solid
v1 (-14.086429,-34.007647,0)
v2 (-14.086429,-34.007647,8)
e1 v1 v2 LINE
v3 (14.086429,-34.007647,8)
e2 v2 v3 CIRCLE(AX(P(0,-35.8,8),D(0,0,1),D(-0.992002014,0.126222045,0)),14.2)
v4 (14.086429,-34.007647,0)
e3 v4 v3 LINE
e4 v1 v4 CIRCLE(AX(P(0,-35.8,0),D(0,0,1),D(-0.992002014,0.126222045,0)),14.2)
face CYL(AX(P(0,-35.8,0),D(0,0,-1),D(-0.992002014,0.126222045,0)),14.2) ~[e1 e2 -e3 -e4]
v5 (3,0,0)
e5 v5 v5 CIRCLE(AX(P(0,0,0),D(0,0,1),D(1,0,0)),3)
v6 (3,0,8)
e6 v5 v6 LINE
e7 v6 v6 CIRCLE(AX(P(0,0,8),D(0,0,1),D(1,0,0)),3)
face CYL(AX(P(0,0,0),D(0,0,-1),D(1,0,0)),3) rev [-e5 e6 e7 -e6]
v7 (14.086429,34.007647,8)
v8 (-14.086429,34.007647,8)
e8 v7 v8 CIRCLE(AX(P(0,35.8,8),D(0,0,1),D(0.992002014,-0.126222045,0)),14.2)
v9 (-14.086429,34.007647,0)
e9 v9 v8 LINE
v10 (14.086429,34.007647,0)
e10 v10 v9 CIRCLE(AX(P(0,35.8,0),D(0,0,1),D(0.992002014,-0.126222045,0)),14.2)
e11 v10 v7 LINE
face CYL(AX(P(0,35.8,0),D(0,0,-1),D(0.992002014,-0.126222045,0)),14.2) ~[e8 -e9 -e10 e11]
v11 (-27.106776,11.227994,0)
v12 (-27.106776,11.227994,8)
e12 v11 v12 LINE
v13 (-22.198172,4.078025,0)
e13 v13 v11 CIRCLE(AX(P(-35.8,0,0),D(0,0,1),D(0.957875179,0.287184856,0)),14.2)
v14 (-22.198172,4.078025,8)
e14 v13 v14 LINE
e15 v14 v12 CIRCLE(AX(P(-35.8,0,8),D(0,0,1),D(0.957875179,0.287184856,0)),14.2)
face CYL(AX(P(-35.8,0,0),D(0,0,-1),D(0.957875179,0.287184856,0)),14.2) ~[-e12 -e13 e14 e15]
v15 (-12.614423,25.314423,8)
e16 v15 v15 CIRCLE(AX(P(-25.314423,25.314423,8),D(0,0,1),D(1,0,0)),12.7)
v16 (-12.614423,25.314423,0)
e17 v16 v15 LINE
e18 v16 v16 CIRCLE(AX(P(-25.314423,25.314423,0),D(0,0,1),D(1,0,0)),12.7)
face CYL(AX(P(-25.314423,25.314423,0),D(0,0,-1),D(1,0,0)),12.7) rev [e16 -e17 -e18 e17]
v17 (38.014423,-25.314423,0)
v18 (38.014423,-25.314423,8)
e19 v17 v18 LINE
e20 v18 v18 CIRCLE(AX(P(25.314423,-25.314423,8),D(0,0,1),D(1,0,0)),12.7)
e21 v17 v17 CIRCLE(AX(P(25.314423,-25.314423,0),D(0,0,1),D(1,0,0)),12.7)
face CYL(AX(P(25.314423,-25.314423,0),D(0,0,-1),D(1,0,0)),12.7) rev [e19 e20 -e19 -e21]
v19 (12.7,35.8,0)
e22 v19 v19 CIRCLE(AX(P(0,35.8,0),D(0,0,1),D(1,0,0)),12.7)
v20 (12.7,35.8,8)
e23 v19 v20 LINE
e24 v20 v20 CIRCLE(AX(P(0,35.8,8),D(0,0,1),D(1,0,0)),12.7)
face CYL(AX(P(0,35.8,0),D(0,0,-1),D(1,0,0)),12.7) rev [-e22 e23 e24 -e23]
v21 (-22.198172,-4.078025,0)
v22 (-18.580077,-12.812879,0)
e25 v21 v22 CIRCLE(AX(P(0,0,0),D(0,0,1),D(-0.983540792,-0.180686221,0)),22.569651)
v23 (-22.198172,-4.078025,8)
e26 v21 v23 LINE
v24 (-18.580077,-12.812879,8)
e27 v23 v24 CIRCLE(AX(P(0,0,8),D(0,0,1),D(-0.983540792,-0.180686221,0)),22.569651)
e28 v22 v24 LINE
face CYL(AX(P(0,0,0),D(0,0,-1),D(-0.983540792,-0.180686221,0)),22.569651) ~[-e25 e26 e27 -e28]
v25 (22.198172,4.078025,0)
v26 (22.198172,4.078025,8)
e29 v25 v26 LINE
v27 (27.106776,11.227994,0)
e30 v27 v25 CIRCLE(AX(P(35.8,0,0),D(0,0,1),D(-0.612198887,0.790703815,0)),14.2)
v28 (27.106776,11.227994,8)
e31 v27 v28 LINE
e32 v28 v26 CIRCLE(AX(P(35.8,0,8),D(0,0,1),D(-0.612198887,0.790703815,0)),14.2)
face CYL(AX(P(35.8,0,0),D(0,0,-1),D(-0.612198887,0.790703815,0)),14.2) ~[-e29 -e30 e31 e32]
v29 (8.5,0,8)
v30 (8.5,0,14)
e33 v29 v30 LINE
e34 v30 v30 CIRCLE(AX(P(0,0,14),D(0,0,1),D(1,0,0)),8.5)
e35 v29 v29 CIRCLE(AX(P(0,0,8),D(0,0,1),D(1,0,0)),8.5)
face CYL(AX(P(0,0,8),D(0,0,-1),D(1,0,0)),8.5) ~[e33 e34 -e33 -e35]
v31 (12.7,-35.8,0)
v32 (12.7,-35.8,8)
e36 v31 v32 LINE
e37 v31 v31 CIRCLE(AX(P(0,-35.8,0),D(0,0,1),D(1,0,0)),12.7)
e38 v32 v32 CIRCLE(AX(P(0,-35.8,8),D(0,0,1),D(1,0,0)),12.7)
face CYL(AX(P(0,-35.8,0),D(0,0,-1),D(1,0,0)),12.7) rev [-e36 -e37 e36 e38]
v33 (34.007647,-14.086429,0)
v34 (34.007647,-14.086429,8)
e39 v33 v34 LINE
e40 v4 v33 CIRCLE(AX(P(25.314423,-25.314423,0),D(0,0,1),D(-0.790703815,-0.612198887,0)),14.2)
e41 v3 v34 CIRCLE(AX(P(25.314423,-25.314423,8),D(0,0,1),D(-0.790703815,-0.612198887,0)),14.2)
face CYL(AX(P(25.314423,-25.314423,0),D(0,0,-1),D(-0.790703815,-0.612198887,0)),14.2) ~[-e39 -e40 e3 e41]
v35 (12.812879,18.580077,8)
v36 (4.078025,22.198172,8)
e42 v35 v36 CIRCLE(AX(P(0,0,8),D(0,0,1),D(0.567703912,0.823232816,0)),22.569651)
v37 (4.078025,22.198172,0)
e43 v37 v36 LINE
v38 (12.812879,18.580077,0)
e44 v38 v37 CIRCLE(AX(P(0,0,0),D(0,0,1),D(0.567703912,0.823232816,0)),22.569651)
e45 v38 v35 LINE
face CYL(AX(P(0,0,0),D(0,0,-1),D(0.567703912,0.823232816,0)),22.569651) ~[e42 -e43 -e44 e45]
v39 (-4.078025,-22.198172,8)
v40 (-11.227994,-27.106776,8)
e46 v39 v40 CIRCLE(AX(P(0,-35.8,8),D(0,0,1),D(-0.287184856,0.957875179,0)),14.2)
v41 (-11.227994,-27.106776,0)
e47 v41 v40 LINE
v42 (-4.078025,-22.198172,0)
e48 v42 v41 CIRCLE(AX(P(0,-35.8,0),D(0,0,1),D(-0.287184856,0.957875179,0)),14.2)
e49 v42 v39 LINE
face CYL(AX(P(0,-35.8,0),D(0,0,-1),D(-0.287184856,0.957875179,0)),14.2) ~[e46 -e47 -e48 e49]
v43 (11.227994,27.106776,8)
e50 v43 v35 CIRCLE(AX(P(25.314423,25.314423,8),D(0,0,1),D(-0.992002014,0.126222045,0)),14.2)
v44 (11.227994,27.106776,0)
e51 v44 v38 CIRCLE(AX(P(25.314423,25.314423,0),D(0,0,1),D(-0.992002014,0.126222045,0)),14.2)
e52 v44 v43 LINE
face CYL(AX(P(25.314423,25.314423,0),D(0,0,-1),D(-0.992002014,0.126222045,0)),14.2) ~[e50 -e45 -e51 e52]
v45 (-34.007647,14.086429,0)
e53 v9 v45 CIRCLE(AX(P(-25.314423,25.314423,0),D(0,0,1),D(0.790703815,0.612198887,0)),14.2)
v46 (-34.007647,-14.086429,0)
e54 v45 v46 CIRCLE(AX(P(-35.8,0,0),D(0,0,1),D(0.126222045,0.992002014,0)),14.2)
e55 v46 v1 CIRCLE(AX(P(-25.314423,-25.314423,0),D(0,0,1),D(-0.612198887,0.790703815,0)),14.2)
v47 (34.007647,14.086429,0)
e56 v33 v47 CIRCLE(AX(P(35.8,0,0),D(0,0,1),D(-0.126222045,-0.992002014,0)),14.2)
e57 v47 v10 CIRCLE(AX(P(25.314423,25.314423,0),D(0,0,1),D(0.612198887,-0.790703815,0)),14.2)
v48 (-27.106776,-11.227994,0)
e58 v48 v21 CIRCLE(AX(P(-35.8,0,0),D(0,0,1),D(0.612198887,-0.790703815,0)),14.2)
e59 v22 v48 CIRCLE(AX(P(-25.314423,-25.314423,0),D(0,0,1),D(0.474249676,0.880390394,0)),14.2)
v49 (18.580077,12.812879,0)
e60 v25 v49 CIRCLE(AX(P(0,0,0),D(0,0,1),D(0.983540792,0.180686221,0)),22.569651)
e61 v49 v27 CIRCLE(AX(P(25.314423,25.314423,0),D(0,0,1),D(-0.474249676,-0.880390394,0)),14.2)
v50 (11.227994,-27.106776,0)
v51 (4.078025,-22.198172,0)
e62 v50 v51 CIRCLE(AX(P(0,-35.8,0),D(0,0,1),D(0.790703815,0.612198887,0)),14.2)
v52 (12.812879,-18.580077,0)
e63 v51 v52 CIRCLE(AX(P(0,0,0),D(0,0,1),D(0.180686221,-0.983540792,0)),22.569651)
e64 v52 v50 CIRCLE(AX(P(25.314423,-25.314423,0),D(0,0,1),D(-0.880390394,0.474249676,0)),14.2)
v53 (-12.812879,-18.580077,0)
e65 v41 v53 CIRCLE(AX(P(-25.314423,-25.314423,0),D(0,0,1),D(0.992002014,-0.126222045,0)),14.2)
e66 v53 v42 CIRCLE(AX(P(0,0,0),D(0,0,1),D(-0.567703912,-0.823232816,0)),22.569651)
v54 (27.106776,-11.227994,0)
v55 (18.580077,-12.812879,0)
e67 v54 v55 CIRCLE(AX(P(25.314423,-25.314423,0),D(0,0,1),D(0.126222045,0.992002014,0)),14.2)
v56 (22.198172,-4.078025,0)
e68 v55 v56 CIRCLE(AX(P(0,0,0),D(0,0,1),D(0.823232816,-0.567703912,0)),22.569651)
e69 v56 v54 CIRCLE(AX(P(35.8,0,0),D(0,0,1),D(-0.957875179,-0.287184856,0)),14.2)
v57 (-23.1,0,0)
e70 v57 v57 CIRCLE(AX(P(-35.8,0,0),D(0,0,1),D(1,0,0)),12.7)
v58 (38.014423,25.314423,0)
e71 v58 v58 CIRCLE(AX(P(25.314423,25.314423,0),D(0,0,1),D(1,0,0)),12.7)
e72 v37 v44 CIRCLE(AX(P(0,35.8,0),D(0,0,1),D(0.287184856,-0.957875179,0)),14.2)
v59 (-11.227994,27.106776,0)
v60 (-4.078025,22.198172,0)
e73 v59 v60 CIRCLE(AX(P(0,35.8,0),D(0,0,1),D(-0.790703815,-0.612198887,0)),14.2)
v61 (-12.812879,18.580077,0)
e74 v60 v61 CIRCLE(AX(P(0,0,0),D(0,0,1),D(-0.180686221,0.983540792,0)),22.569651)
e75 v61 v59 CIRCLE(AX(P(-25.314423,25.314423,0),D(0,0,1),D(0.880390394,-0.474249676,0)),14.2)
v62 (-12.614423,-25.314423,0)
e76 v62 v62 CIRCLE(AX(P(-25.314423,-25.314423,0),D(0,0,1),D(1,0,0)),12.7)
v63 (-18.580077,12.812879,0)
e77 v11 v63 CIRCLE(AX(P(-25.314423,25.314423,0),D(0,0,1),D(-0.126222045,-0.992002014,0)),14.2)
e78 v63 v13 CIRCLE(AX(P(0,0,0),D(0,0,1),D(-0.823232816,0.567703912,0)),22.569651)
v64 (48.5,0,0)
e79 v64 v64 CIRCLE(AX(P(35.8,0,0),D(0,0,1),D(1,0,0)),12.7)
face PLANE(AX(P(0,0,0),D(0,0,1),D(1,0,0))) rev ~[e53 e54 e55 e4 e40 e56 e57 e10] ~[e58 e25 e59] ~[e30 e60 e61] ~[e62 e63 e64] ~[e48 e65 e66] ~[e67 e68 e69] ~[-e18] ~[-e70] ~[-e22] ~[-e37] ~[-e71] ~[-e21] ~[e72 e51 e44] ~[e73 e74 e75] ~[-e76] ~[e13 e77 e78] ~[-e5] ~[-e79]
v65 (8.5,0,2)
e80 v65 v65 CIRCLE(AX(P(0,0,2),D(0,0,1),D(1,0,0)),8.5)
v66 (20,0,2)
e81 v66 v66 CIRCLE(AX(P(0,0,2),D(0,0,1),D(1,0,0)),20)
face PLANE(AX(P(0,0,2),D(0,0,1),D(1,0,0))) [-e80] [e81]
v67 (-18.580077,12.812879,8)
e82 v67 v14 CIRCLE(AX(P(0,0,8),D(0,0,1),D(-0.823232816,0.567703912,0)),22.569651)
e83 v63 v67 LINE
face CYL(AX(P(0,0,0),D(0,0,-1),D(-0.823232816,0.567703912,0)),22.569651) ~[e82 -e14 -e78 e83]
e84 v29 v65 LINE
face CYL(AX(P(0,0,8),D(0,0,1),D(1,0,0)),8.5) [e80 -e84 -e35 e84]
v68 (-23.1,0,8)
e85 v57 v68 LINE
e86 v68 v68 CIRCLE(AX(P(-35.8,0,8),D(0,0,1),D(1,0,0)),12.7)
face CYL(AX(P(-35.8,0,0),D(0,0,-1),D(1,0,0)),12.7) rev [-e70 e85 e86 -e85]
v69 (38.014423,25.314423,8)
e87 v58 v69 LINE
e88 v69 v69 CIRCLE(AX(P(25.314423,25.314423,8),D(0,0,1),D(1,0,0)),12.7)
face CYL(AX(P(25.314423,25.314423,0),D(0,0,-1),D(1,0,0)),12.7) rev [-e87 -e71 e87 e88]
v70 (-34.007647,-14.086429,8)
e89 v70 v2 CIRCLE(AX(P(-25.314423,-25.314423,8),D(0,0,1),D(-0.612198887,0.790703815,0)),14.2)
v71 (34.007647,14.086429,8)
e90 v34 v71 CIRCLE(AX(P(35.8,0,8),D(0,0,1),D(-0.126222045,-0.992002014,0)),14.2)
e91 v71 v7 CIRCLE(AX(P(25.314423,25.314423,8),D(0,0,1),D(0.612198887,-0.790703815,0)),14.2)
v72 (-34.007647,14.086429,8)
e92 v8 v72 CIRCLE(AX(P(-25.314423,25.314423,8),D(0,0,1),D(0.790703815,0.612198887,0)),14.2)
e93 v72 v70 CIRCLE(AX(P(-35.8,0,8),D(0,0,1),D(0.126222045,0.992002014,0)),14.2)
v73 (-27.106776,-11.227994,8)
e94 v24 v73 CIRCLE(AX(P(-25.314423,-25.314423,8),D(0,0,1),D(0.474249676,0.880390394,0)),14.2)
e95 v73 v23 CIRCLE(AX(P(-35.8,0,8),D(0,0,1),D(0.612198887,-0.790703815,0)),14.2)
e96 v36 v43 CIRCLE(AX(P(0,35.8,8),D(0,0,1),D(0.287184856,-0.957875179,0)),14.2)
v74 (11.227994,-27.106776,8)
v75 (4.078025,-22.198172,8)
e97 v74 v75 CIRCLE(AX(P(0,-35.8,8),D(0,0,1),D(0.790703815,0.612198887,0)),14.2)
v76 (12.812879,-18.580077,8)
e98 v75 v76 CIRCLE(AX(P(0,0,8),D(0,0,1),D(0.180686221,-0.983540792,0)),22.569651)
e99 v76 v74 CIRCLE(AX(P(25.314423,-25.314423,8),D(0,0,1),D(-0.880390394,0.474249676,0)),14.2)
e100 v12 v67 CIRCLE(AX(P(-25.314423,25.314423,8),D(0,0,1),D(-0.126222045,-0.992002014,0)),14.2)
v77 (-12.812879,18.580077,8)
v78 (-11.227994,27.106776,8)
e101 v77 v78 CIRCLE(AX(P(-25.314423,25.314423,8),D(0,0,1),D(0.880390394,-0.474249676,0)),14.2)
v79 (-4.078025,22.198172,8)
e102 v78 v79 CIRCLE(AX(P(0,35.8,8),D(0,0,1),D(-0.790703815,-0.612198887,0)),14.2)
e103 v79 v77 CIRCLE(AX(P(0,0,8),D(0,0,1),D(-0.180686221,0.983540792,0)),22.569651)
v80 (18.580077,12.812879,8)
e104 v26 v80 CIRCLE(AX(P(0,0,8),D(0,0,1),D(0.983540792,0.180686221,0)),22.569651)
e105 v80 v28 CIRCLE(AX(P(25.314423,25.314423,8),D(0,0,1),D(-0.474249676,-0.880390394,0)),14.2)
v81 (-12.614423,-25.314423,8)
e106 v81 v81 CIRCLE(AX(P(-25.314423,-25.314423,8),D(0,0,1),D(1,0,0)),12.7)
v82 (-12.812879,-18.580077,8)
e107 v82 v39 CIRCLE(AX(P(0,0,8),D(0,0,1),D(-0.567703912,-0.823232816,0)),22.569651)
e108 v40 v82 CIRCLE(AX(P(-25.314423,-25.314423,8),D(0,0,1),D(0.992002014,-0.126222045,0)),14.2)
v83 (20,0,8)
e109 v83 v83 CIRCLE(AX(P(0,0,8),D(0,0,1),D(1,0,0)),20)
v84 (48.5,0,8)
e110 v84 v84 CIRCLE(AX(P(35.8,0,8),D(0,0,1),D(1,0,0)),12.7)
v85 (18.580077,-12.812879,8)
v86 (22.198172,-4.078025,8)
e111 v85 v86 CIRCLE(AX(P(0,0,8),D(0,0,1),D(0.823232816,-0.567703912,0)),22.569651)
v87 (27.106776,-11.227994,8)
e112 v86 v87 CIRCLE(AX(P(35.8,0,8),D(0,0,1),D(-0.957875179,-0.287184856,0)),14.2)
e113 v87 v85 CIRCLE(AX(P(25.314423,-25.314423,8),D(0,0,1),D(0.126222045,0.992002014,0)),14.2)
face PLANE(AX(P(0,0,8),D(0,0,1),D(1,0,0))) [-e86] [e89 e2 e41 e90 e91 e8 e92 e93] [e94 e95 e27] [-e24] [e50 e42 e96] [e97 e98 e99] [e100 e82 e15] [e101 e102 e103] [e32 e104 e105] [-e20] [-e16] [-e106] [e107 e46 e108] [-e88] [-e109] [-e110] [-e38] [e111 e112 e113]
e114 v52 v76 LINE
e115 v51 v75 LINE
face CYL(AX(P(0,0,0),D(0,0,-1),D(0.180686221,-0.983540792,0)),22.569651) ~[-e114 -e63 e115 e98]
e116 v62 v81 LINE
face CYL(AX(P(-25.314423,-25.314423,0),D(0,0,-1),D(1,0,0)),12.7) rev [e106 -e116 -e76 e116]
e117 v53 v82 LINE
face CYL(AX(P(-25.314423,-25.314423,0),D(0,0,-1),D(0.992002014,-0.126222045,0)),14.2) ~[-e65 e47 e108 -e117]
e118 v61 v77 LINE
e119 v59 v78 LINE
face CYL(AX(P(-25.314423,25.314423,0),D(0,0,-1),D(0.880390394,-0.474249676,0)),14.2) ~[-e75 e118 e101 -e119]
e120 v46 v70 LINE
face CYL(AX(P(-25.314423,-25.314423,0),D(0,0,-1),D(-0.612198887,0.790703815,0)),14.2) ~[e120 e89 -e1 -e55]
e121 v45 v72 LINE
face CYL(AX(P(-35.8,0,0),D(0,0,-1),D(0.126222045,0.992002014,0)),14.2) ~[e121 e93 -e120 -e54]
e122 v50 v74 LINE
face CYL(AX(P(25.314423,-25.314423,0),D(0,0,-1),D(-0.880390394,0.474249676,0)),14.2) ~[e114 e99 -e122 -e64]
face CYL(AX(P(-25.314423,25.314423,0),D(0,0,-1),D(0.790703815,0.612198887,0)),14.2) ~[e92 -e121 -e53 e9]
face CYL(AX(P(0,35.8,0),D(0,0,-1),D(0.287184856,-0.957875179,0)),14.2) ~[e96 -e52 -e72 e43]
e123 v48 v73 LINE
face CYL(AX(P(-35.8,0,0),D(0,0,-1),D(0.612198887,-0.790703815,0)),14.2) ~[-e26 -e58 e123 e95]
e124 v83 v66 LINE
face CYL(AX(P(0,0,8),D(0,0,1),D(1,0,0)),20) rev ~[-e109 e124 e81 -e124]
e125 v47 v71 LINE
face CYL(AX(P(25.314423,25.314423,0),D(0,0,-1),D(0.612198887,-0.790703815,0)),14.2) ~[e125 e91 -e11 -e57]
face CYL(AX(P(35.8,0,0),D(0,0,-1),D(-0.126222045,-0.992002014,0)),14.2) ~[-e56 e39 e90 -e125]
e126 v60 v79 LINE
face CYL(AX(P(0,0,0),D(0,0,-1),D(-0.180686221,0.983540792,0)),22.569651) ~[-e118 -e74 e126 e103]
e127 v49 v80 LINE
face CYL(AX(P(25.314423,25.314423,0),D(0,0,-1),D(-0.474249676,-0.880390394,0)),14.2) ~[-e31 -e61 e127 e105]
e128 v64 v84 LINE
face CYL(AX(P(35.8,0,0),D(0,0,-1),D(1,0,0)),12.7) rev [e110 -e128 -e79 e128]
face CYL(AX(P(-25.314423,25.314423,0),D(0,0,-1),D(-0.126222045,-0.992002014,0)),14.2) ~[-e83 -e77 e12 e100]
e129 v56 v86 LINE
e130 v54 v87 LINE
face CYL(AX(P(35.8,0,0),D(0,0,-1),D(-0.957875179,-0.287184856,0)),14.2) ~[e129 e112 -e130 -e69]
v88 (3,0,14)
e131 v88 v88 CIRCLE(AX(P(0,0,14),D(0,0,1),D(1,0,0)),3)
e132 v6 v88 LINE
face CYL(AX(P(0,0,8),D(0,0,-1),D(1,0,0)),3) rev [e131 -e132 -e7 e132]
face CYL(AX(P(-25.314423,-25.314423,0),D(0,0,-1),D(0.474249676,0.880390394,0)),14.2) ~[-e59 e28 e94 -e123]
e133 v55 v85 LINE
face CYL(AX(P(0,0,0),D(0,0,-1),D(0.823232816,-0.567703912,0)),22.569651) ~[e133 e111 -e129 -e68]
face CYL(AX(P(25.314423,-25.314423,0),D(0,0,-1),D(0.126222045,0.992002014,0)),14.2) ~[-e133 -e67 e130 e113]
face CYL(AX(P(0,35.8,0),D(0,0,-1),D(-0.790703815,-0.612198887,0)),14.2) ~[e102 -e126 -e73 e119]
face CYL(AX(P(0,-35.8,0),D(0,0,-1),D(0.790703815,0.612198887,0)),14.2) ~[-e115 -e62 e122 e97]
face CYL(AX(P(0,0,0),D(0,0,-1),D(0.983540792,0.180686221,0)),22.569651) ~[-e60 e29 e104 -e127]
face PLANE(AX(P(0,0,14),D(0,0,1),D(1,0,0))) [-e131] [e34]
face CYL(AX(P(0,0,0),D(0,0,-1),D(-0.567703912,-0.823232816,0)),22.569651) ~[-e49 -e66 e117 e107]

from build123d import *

# Parameters (mm, degrees)
SKETCH1_R           = 3
SKETCH1_R_2         = 12.7
BOSS_EXTRUDE1_DEPTH = 8
SKETCH4_R           = 20
SKETCH4_R_2         = 8.5
CUT_EXTRUDE2_DEPTH  = 6
SKETCH5_R           = 8.5
SKETCH5_R_2         = 3
BOSS_EXTRUDE3_DEPTH = 6


with BuildPart() as part:
    # Sketch1 → Boss-Extrude1 (new body)
    with BuildSketch(Plane.XY):
        with BuildLine():
            ThreePointArc((-14.086428596, 34.007646961), (-35.355339059, 35.355339059), (-34.007646961, 14.086428596))
            ThreePointArc((-34.007646961, 14.086428596), (-50, 0), (-34.007646961, -14.086428596))
            ThreePointArc((-34.007646961, -14.086428596), (-35.355339059, -35.355339059), (-14.086428596, -34.007646961))
            ThreePointArc((-14.086428596, -34.007646961), (0, -50), (14.086428596, -34.007646961))
            ThreePointArc((14.086428596, -34.007646961), (35.355339059, -35.355339059), (34.007646961, -14.086428596))
            ThreePointArc((34.007646961, -14.086428596), (50, 0), (34.007646961, 14.086428596))
            ThreePointArc((34.007646961, 14.086428596), (35.355339059, 35.355339059), (14.086428596, 34.007646961))
            ThreePointArc((14.086428596, 34.007646961), (0, 50), (-14.086428596, 34.007646961))
        make_face()
        Circle(SKETCH1_R, mode=Mode.SUBTRACT)
        with Locations((0, 35.8)):
            Circle(SKETCH1_R_2, mode=Mode.SUBTRACT)
        with Locations((25.314422766, 25.314422766)):
            Circle(SKETCH1_R_2, mode=Mode.SUBTRACT)
        with Locations((35.8, 0)):
            Circle(SKETCH1_R_2, mode=Mode.SUBTRACT)
        with Locations((25.314422766, -25.314422766)):
            Circle(SKETCH1_R_2, mode=Mode.SUBTRACT)
        with Locations((0, -35.8)):
            Circle(SKETCH1_R_2, mode=Mode.SUBTRACT)
        with Locations((-25.314422766, -25.314422766)):
            Circle(SKETCH1_R_2, mode=Mode.SUBTRACT)
        with Locations((-35.8, 0)):
            Circle(SKETCH1_R_2, mode=Mode.SUBTRACT)
        with Locations((-25.314422766, 25.314422766)):
            Circle(SKETCH1_R_2, mode=Mode.SUBTRACT)
        with BuildLine():
            ThreePointArc((-11.227994171, 27.106775805), (-8.03692429, 24.093256305), (-4.078024952, 22.198172458))
            ThreePointArc((-4.078024952, 22.198172458), (-8.637031526, 20.85163865), (-12.812879177, 18.580077372))
            ThreePointArc((-12.812879177, 18.580077372), (-11.353541248, 22.719468579), (-11.227994171, 27.106775805))
        make_face(mode=Mode.SUBTRACT)
        with BuildLine():
            ThreePointArc((11.227994171, 27.106775805), (11.353541248, 22.719468579), (12.812879177, 18.580077372))
            ThreePointArc((12.812879177, 18.580077372), (8.637031526, 20.85163865), (4.078024952, 22.198172458))
            ThreePointArc((4.078024952, 22.198172458), (8.03692429, 24.093256305), (11.227994171, 27.106775805))
        make_face(mode=Mode.SUBTRACT)
        with BuildLine():
            ThreePointArc((27.106775805, 11.227994171), (24.093256305, 8.03692429), (22.198172458, 4.078024952))
            ThreePointArc((22.198172458, 4.078024952), (20.85163865, 8.637031526), (18.580077372, 12.812879177))
            ThreePointArc((18.580077372, 12.812879177), (22.719468579, 11.353541248), (27.106775805, 11.227994171))
        make_face(mode=Mode.SUBTRACT)
        with BuildLine():
            ThreePointArc((27.106775805, -11.227994171), (22.719468579, -11.353541248), (18.580077372, -12.812879177))
            ThreePointArc((18.580077372, -12.812879177), (20.85163865, -8.637031526), (22.198172458, -4.078024952))
            ThreePointArc((22.198172458, -4.078024952), (24.093256305, -8.03692429), (27.106775805, -11.227994171))
        make_face(mode=Mode.SUBTRACT)
        with BuildLine():
            ThreePointArc((11.227994171, -27.106775805), (8.03692429, -24.093256305), (4.078024952, -22.198172458))
            ThreePointArc((4.078024952, -22.198172458), (8.637031526, -20.85163865), (12.812879177, -18.580077372))
            ThreePointArc((12.812879177, -18.580077372), (11.353541248, -22.719468579), (11.227994171, -27.106775805))
        make_face(mode=Mode.SUBTRACT)
        with BuildLine():
            ThreePointArc((-11.227994171, -27.106775805), (-11.353541248, -22.719468579), (-12.812879177, -18.580077372))
            ThreePointArc((-12.812879177, -18.580077372), (-8.637031526, -20.85163865), (-4.078024952, -22.198172458))
            ThreePointArc((-4.078024952, -22.198172458), (-8.03692429, -24.093256305), (-11.227994171, -27.106775805))
        make_face(mode=Mode.SUBTRACT)
        with BuildLine():
            ThreePointArc((-27.106775805, -11.227994171), (-24.093256305, -8.03692429), (-22.198172458, -4.078024952))
            ThreePointArc((-22.198172458, -4.078024952), (-20.85163865, -8.637031526), (-18.580077372, -12.812879177))
            ThreePointArc((-18.580077372, -12.812879177), (-22.719468579, -11.353541248), (-27.106775805, -11.227994171))
        make_face(mode=Mode.SUBTRACT)
        with BuildLine():
            ThreePointArc((-18.580077372, 12.812879177), (-20.85163865, 8.637031526), (-22.198172458, 4.078024952))
            ThreePointArc((-22.198172458, 4.078024952), (-24.093256305, 8.03692429), (-27.106775805, 11.227994171))
            ThreePointArc((-27.106775805, 11.227994171), (-22.719468579, 11.353541248), (-18.580077372, 12.812879177))
        make_face(mode=Mode.SUBTRACT)
    extrude(amount=BOSS_EXTRUDE1_DEPTH)

    # Sketch4 → Cut-Extrude2 (cut)
    with BuildSketch(Plane.XY.offset(8)):
        Circle(SKETCH4_R)
        Circle(SKETCH4_R_2, mode=Mode.SUBTRACT)
    extrude(amount=-CUT_EXTRUDE2_DEPTH, mode=Mode.SUBTRACT)

    # Sketch5 → Boss-Extrude3 (add)
    with BuildSketch(Plane.XY.offset(8)):
        Circle(SKETCH5_R)
        Circle(SKETCH5_R_2, mode=Mode.SUBTRACT)
    extrude(amount=BOSS_EXTRUDE3_DEPTH)


solid = part.part
